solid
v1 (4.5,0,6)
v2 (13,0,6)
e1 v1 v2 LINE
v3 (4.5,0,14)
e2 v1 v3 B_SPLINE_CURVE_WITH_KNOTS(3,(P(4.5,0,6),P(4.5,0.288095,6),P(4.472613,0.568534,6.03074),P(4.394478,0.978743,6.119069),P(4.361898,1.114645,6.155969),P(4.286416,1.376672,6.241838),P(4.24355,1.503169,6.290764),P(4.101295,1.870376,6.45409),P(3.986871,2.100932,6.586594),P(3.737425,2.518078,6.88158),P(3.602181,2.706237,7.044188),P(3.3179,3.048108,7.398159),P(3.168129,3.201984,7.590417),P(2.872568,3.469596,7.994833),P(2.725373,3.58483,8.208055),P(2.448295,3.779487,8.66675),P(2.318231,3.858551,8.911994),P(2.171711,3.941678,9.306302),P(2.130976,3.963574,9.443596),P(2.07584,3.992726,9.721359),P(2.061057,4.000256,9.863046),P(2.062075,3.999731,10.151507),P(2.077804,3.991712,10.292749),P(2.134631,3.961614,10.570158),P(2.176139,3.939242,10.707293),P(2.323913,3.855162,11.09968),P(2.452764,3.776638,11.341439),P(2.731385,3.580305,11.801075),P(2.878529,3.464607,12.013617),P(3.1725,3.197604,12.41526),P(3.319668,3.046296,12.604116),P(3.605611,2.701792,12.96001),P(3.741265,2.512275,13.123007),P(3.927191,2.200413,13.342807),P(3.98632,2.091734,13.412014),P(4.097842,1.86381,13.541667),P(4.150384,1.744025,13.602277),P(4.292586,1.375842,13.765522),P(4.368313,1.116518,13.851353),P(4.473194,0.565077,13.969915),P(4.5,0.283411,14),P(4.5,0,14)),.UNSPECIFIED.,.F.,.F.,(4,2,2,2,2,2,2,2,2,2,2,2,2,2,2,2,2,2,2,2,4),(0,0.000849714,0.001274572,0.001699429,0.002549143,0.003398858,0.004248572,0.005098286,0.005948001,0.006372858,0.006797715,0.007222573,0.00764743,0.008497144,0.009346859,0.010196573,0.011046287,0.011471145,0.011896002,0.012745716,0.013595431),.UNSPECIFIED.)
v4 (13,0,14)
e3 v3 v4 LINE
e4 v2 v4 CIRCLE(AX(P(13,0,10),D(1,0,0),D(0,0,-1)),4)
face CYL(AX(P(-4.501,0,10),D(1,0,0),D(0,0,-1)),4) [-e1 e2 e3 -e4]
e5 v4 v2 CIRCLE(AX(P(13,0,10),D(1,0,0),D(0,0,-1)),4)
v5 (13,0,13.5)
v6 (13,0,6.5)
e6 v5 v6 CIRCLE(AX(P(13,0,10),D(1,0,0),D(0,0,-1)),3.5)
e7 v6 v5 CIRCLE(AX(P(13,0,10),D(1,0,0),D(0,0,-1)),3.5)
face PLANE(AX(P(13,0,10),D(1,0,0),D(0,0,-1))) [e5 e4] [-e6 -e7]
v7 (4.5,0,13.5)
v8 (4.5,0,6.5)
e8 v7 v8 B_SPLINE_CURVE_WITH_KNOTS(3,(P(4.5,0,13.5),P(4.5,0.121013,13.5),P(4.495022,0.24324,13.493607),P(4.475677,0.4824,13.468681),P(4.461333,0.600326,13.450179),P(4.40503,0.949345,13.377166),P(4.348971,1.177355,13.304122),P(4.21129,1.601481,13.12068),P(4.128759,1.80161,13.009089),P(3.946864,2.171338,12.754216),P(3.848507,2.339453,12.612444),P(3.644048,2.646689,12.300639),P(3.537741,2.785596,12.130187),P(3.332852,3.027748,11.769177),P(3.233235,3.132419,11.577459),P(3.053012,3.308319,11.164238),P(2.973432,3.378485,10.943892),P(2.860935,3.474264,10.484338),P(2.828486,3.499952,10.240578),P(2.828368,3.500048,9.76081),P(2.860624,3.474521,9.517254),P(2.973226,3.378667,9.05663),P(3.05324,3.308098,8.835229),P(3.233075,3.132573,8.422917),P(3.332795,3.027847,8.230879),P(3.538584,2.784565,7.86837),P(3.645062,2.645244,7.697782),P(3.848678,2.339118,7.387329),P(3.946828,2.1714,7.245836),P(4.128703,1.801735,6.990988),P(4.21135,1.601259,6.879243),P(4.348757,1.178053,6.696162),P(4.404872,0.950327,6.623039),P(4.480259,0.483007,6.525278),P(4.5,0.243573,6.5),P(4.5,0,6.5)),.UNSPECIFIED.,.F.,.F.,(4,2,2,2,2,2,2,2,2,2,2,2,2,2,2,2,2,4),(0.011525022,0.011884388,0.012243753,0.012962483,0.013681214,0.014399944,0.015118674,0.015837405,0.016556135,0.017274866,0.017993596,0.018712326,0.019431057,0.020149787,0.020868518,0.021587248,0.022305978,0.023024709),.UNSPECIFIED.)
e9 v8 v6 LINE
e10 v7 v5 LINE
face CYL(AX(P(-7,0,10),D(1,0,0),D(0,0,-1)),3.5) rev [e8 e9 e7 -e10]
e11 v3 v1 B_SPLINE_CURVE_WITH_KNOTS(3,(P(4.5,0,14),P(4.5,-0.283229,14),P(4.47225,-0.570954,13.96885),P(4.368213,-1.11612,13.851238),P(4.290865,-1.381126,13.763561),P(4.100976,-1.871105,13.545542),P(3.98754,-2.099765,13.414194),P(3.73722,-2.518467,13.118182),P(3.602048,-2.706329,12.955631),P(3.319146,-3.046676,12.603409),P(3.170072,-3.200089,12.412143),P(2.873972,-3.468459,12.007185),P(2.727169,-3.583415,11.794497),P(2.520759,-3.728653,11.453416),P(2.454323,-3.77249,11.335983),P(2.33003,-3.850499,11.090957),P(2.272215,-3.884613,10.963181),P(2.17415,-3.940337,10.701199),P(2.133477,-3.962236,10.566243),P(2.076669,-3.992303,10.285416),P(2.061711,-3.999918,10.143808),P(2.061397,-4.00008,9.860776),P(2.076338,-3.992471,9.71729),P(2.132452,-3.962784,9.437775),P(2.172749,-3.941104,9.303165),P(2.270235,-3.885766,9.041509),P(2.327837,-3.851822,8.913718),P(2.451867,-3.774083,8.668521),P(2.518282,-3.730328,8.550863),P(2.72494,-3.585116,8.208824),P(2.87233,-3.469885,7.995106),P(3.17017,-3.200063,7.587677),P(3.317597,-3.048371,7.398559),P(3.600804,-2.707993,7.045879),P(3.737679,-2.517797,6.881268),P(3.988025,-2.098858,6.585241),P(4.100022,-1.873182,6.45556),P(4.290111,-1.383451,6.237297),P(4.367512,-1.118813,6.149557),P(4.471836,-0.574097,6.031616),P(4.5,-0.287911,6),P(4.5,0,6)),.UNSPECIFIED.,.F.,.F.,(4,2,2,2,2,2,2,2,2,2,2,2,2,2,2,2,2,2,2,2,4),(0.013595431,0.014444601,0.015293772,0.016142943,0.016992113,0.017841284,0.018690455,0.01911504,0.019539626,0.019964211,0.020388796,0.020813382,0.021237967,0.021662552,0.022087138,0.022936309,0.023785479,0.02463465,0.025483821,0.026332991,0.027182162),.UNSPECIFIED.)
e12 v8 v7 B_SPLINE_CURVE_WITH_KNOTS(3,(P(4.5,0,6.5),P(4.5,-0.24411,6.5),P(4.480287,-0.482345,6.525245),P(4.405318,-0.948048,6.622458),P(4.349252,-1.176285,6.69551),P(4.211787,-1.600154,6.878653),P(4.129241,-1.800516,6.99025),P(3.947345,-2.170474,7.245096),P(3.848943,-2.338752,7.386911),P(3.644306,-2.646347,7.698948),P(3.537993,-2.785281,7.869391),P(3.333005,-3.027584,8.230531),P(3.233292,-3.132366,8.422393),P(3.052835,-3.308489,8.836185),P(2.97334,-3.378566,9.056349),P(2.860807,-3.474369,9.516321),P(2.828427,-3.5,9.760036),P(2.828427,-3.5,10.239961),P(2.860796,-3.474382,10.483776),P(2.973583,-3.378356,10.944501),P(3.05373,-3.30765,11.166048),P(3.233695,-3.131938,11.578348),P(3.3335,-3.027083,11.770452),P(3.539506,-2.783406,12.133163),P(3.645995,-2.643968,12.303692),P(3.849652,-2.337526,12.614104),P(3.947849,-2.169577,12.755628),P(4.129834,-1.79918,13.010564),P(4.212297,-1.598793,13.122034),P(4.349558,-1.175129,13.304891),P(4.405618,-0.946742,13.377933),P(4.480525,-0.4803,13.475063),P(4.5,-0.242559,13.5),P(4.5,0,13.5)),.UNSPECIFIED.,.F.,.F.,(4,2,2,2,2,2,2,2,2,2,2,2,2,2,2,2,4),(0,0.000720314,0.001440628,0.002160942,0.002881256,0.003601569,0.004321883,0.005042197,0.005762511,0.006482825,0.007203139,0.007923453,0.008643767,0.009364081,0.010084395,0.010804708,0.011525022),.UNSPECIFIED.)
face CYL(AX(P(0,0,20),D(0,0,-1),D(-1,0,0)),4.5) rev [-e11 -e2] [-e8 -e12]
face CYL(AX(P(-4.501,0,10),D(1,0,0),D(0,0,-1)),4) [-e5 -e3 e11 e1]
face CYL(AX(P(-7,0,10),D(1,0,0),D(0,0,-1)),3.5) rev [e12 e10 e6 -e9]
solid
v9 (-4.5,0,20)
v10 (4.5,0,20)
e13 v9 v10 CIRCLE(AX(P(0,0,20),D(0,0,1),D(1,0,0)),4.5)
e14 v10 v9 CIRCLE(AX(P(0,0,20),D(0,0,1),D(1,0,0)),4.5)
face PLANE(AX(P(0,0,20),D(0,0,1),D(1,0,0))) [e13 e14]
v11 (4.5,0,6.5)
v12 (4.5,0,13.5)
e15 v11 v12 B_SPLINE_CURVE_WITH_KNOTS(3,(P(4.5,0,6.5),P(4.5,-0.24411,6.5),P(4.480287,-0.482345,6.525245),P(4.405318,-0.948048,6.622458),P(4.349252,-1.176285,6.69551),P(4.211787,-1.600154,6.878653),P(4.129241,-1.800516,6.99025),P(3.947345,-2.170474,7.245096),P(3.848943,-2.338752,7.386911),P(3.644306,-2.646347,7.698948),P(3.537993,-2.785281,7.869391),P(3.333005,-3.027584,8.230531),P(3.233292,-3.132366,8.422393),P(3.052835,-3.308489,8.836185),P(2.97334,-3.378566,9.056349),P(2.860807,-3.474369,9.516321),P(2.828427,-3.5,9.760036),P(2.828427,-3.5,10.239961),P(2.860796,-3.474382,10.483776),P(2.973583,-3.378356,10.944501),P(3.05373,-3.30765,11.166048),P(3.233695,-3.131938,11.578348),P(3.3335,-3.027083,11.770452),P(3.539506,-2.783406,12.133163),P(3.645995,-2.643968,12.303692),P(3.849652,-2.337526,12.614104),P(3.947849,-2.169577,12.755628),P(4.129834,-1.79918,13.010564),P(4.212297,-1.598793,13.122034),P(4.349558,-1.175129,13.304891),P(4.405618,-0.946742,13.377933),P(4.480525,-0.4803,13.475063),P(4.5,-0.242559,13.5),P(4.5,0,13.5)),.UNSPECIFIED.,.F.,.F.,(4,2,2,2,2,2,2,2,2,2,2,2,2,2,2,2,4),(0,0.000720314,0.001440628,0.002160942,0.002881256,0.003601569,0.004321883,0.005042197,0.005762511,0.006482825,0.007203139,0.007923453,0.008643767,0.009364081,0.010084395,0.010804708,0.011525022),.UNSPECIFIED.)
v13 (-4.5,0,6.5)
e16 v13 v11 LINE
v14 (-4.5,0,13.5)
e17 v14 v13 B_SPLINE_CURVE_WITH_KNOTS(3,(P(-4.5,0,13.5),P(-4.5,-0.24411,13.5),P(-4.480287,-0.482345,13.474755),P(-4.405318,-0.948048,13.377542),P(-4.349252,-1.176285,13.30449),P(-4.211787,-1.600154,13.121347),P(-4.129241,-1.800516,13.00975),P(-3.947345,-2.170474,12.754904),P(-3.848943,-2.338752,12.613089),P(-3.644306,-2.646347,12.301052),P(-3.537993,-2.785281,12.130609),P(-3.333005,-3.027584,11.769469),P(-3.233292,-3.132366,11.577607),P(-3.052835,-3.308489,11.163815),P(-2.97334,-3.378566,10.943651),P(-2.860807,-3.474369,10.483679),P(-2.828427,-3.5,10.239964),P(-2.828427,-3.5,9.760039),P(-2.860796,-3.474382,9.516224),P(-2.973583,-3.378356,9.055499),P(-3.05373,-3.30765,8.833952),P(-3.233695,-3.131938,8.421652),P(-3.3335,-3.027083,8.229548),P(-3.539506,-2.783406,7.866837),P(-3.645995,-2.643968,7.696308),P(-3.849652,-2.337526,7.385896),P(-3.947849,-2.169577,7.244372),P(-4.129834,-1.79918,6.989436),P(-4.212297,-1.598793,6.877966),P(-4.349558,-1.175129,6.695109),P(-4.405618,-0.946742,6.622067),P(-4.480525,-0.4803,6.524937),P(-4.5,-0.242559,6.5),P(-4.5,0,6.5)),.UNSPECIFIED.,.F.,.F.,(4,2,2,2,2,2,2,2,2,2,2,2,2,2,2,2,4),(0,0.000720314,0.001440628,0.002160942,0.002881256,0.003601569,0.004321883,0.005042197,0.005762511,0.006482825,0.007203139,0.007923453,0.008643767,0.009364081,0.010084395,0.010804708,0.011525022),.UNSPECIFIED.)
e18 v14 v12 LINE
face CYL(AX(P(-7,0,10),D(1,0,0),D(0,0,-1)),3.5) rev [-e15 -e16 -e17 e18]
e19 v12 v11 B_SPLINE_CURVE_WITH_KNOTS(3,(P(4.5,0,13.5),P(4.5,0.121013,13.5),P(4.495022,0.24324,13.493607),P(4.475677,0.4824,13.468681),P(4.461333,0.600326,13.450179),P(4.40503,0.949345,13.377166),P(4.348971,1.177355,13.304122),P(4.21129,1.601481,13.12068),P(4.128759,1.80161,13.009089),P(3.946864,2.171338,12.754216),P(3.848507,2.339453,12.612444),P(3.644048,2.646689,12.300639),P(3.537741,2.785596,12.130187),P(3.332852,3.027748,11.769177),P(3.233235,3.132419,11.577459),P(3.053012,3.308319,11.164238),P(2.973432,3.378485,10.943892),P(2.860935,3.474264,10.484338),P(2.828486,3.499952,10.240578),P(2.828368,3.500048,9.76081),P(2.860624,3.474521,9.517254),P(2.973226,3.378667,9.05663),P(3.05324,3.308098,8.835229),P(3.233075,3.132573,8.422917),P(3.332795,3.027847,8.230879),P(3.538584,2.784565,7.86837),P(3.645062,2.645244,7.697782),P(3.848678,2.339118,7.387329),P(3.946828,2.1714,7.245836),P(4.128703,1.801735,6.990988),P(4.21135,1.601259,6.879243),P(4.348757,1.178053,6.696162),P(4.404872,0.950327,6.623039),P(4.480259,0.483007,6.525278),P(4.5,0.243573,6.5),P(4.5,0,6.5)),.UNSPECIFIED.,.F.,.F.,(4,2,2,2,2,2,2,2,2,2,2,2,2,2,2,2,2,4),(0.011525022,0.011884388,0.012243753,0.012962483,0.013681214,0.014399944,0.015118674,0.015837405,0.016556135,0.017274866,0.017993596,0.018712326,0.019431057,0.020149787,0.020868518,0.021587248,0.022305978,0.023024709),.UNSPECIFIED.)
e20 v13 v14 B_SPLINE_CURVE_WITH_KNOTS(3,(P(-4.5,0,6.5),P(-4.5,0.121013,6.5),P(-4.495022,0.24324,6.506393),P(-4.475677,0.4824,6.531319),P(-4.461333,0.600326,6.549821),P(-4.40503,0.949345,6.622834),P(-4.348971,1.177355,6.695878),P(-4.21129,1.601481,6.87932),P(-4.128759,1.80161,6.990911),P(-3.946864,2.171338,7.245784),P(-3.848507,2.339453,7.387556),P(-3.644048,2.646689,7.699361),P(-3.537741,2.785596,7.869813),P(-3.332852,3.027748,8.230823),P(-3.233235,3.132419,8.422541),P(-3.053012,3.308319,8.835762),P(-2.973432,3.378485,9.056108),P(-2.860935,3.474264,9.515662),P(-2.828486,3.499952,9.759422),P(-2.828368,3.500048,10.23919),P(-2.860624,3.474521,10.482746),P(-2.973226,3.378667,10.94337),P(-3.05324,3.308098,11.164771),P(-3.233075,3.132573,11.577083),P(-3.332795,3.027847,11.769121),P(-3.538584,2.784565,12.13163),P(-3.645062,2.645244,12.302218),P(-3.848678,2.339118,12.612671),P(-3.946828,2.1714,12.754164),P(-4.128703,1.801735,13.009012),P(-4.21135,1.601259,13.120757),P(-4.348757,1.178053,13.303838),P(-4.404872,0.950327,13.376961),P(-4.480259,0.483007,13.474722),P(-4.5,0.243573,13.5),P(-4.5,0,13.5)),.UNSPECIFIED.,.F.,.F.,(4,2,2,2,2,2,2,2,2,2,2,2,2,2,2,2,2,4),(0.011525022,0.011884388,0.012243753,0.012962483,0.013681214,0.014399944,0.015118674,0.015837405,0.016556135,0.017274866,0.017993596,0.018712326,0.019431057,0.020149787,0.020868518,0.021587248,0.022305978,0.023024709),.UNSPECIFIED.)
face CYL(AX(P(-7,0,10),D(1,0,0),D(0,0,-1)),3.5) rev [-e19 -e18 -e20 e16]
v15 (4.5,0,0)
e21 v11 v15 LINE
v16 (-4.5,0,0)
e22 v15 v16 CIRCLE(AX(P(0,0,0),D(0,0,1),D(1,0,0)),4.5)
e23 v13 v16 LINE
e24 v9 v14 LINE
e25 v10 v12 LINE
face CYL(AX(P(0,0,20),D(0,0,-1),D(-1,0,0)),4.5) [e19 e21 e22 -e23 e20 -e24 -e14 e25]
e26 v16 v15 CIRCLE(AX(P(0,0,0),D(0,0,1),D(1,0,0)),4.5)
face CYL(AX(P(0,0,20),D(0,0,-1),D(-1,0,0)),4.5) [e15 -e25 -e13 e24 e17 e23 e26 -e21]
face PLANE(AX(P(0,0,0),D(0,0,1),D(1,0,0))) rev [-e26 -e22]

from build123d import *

# Parameters (mm, degrees)
SKETCH_1_R           = 4.5
EXTRUDE_1_DEPTH      = 20
EXTRUDE_2_REACH      = 28.954
EXTRUDE_2_END_RADIUS = 4.5
SKETCH_2_R           = 4
SKETCH_3_R           = 3.5
CUT_EXTRUDE_1_DEPTH  = 20


with BuildPart() as part:
    # 草图1 → 凸台-拉伸1 (new body)
    with BuildSketch(Plane.XY):
        Circle(SKETCH_1_R)
    extrude(amount=EXTRUDE_1_DEPTH)


with BuildPart() as body_2:
    # 凸台-拉伸2: up to this cylinder (the profile starts outside it)
    extrude_2_end = Plane(origin=(0, 0, 10), z_dir=(0, 0, -1)) * Cylinder(EXTRUDE_2_END_RADIUS, 67.908, mode=Mode.PRIVATE)
    # 草图2 → 凸台-拉伸2 (new, up to the surface)
    with BuildSketch(Plane(origin=(13, 0, 0), x_dir=(0, 0, -1), z_dir=(1, 0, 0)), mode=Mode.PRIVATE) as extrude_2_sk1:
        with Locations((-10, 0)):
            Circle(SKETCH_2_R)
    extrude_2_tool1 = extrude(extrude_2_sk1.sketch, amount=-EXTRUDE_2_REACH, mode=Mode.PRIVATE) - extrude_2_end
    add(extrude_2_tool1.solids().sort_by_distance((13, 0, 10))[0])


with BuildPart() as cut_extrude_1_tool:
    # 草图3 → 切除-拉伸1 (new body)
    with BuildSketch(Plane(origin=(13, 0, 0), x_dir=(0, 0, -1), z_dir=(1, 0, 0))):
        with Locations((-10, 0)):
            Circle(SKETCH_3_R)
    extrude(amount=-CUT_EXTRUDE_1_DEPTH)


with BuildPart() as part_1:
    add(part.part)

    # 切除-拉伸1: cut by cut_extrude_1_tool
    add(cut_extrude_1_tool.part, mode=Mode.SUBTRACT)


with BuildPart() as body_2_1:
    add(body_2.part)

    # 切除-拉伸1: cut by cut_extrude_1_tool
    add(cut_extrude_1_tool.part, mode=Mode.SUBTRACT)


solid = Compound([part_1.part, body_2_1.part])
